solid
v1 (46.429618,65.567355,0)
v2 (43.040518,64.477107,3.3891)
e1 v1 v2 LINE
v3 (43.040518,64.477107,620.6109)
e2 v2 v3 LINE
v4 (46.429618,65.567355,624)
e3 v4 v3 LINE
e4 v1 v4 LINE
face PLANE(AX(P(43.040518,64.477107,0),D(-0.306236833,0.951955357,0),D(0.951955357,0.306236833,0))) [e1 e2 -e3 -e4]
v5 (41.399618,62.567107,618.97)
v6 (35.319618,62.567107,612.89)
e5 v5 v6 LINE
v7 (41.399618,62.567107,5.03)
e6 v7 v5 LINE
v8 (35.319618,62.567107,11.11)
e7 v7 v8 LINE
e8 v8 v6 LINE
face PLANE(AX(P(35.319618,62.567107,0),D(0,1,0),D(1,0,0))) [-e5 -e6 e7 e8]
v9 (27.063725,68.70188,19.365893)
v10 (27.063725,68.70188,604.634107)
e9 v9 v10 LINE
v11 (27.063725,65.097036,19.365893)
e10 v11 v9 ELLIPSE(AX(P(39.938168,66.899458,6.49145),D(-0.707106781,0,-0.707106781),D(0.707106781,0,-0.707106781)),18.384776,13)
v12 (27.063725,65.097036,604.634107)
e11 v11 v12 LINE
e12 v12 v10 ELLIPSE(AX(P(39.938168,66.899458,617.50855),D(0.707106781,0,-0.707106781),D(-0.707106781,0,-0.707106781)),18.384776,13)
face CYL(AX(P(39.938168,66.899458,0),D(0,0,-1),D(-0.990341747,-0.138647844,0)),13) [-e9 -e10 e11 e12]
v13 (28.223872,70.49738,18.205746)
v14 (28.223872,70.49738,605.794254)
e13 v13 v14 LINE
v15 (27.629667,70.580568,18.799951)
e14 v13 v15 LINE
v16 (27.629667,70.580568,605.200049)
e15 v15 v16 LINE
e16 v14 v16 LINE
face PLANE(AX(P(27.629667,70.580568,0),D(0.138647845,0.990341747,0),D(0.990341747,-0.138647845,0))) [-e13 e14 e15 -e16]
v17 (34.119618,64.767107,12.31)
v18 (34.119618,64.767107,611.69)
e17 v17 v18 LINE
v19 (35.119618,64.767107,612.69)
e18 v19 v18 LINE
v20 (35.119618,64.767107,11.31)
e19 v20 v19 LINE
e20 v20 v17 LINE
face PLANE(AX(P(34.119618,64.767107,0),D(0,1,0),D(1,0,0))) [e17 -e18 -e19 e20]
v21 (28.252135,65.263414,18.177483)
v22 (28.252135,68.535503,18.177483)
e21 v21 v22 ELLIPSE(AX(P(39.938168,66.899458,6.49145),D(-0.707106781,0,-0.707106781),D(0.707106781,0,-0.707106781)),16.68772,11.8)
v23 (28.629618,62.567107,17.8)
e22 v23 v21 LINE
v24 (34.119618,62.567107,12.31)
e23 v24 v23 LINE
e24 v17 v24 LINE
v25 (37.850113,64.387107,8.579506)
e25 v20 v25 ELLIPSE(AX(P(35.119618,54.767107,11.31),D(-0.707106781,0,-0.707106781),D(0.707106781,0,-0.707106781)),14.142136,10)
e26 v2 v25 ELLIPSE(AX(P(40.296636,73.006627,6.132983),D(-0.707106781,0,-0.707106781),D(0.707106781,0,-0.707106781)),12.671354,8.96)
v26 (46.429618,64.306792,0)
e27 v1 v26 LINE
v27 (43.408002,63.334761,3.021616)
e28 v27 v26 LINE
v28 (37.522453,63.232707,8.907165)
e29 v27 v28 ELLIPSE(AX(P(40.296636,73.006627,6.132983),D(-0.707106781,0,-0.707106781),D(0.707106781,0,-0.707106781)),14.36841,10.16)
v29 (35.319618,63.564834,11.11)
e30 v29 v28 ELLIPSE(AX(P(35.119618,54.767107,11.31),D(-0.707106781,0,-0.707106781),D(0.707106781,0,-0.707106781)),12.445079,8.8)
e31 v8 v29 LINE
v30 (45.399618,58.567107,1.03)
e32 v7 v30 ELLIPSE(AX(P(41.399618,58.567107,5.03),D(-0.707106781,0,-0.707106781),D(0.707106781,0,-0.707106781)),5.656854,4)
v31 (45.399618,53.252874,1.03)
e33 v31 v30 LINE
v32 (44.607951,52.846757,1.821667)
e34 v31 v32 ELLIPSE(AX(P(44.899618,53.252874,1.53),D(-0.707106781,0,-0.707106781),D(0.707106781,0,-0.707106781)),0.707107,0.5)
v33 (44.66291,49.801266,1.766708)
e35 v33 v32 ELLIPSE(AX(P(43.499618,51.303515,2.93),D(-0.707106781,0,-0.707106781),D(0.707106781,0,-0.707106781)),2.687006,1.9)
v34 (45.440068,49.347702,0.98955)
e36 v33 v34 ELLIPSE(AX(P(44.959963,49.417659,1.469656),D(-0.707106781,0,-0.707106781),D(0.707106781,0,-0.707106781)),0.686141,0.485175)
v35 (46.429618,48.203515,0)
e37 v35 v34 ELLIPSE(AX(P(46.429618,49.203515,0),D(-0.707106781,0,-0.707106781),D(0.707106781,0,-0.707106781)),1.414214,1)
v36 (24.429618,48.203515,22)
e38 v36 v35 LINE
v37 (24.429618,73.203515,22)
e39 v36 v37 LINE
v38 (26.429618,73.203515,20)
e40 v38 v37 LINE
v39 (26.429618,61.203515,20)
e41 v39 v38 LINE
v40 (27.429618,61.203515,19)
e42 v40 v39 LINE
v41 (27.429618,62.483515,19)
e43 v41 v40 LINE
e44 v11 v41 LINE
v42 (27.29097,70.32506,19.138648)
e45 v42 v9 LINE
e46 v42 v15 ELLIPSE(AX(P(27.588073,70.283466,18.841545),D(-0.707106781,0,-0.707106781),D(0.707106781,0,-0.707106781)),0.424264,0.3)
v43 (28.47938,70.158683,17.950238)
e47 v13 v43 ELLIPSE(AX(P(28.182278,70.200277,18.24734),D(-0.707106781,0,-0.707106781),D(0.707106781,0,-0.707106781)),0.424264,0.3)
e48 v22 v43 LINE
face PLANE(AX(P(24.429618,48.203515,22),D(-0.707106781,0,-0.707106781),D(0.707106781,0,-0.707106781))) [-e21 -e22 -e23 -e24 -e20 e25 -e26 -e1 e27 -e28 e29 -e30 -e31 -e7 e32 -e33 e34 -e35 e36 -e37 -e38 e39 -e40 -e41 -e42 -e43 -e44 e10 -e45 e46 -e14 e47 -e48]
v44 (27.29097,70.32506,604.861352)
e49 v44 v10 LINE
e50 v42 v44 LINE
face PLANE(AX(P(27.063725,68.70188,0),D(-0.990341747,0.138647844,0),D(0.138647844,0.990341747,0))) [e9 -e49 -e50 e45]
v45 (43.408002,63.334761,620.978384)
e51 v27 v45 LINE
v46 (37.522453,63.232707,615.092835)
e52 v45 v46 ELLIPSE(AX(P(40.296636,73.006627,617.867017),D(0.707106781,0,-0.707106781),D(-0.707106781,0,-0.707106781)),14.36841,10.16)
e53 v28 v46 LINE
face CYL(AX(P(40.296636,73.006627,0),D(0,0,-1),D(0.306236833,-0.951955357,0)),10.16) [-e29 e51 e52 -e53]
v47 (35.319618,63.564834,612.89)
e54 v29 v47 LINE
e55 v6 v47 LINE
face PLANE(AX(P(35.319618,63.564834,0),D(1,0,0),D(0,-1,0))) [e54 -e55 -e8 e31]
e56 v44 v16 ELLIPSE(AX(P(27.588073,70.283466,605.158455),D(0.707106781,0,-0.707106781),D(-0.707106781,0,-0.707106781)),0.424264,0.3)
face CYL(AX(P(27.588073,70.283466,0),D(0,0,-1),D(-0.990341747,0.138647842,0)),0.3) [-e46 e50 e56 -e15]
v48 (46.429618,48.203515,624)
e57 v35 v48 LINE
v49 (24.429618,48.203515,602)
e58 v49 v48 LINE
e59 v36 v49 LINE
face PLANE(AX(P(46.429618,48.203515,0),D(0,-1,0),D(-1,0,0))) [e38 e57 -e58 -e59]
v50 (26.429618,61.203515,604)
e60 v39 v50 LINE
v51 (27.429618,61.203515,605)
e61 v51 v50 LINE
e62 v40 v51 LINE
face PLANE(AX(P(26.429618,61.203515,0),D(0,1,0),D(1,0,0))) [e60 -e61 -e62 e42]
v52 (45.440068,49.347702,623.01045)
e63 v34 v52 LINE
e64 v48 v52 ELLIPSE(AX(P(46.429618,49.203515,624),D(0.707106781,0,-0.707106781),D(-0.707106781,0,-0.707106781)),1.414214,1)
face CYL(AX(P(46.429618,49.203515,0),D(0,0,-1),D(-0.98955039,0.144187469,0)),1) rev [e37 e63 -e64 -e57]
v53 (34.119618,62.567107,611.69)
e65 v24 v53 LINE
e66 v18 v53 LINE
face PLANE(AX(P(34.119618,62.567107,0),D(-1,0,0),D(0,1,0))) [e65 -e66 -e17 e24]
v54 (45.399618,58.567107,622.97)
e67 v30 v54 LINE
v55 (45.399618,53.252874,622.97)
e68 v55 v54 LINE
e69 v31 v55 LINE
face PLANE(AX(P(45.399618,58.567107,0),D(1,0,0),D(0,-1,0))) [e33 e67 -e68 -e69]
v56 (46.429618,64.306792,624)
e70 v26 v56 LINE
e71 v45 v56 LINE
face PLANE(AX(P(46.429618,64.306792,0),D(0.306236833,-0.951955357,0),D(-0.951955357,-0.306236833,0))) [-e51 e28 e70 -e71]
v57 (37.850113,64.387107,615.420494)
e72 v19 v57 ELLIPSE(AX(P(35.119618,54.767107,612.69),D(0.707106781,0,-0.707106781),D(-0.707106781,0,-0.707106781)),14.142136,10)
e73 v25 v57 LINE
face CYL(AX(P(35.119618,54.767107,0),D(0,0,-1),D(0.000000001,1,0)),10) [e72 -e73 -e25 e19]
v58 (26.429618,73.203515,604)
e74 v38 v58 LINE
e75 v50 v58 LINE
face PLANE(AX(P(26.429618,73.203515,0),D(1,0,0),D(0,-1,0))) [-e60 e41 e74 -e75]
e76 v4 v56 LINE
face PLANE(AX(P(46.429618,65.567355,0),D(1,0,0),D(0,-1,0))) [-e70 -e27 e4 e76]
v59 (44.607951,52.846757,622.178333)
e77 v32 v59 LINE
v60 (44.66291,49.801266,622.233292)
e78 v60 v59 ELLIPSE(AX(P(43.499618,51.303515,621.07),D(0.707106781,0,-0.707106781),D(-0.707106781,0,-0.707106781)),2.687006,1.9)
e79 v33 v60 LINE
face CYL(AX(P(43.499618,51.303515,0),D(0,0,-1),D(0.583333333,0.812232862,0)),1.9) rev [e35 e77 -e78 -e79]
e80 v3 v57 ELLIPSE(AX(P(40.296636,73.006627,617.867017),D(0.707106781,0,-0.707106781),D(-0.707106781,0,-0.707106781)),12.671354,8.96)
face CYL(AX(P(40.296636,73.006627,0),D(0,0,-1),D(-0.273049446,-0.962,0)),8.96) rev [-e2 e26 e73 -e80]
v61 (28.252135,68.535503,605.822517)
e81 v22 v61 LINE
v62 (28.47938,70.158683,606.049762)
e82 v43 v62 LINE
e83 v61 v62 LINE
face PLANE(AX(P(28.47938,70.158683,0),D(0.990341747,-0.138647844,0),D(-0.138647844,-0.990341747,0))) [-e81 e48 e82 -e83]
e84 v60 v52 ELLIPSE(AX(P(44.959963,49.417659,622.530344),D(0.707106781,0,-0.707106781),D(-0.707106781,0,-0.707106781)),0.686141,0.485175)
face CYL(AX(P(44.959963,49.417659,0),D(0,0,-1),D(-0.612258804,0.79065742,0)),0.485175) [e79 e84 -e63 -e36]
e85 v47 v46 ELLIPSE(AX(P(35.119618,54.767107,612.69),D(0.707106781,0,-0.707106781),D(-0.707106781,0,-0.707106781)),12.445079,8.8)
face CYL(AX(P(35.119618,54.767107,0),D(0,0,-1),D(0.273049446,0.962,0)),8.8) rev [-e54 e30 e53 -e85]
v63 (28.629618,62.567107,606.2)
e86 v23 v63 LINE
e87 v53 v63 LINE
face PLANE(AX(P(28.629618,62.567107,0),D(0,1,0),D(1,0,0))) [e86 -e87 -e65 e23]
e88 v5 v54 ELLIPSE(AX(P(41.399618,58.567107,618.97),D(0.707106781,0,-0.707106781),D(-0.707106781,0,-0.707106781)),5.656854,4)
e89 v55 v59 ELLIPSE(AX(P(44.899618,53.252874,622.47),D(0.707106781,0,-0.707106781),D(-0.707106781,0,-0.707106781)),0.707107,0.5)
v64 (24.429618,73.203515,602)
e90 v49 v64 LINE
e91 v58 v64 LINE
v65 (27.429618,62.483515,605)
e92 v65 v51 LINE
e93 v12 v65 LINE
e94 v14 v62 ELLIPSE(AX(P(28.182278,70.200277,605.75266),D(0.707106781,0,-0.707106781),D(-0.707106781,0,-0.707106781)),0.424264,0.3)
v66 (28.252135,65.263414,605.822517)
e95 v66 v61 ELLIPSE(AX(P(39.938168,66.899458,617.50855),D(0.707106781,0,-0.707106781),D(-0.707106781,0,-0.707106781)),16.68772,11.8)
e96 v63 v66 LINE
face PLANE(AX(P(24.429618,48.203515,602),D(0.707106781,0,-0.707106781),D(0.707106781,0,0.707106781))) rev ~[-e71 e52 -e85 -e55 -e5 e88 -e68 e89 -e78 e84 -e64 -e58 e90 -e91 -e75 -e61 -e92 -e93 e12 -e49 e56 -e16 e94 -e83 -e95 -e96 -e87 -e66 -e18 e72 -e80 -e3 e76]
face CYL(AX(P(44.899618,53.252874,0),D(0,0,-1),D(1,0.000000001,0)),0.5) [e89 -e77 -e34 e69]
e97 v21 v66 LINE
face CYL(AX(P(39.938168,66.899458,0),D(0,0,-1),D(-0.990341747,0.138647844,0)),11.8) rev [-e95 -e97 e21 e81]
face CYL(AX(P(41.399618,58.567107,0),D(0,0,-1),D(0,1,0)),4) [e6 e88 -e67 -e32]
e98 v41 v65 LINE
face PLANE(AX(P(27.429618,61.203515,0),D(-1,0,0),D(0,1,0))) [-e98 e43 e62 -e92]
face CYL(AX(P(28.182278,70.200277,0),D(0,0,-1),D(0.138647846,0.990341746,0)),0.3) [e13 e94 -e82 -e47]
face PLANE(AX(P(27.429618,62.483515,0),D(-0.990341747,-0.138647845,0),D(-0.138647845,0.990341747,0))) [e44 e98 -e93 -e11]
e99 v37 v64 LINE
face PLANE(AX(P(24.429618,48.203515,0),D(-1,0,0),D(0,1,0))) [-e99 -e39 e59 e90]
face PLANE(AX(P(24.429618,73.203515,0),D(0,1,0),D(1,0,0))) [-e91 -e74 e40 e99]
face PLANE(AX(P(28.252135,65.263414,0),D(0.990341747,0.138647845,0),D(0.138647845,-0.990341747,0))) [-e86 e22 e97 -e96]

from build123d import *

# Parameters (mm, degrees)
EXTRUDE1_DEPTH = 624
EXTRUDE2_DEPTH = 30


with BuildPart() as part:
    # Sketch2 → Extrude1 (new body)
    with BuildSketch(Plane.XY):
        with BuildLine():
            Line((27.429618111, 61.203514875), (27.429618111, 62.483514875))
            Line((27.429618111, 62.483514875), (27.063725093, 65.097036429))
            ThreePointArc((27.063725093, 65.097036429), (26.9381678, 66.899458408), (27.063725093, 68.701880387))
            Line((27.063725093, 68.701880387), (27.290970266, 70.325060195))
            ThreePointArc((27.290970266, 70.325060195), (27.40740123, 70.522960701), (27.629667144, 70.580568366))
            Line((27.629667144, 70.580568366), (28.223872192, 70.497379659))
            ThreePointArc((28.223872192, 70.497379659), (28.421772697, 70.380948695), (28.479380362, 70.158682782))
            Line((28.479380362, 70.158682782), (28.252135189, 68.535502974))
            ThreePointArc((28.252135189, 68.535502974), (28.1381678, 66.899458408), (28.252135189, 65.263413843))
            Line((28.252135189, 65.263413843), (28.629618111, 62.56710726))
            Line((28.629618111, 62.56710726), (34.119618111, 62.56710726))
            Line((34.119618111, 62.56710726), (34.119618111, 64.76710726))
            Line((34.119618111, 64.76710726), (35.119618111, 64.76710726))
            ThreePointArc((35.119618111, 64.76710726), (36.498022986, 64.671651671), (37.850112572, 64.38710726))
            ThreePointArc((37.850112572, 64.38710726), (40.451975855, 64.047973934), (43.040517634, 64.47710726))
            Line((43.040517634, 64.47710726), (46.429618111, 65.567355231))
            Line((46.429618111, 65.567355231), (46.429618111, 64.306791917))
            Line((46.429618111, 64.306791917), (43.408001834, 63.334760831))
            ThreePointArc((43.408001834, 63.334760831), (40.472780352, 62.848154292), (37.522453236, 63.23270726))
            ThreePointArc((37.522453236, 63.23270726), (36.431587911, 63.468758554), (35.319618111, 63.564834239))
            Line((35.319618111, 63.564834239), (35.319618111, 62.56710726))
            Line((35.319618111, 62.56710726), (41.399618111, 62.56710726))
            ThreePointArc((41.399618111, 62.56710726), (44.228045236, 61.395534384), (45.399618111, 58.56710726))
            Line((45.399618111, 58.56710726), (45.399618111, 53.252873744))
            ThreePointArc((45.399618111, 53.252873744), (45.127835843, 52.807995483), (44.607951444, 52.846757313))
            ThreePointArc((44.607951444, 52.846757313), (41.599927405, 51.269233396), (44.662909839, 49.801265776))
            ThreePointArc((44.662909839, 49.801265776), (45.204517239, 49.836690545), (45.440067721, 49.347702344))
            ThreePointArc((45.440067721, 49.347702344), (45.673249329, 48.549369428), (46.429618111, 48.203514875))
            Line((46.429618111, 48.203514875), (24.429618111, 48.203514875))
            Line((24.429618111, 48.203514875), (24.429618111, 73.203514875))
            Line((24.429618111, 73.203514875), (26.429618111, 73.203514875))
            Line((26.429618111, 73.203514875), (26.429618111, 61.203514875))
            Line((26.429618111, 61.203514875), (27.429618111, 61.203514875))
        make_face()
    extrude(amount=EXTRUDE1_DEPTH)

    # Sketch3 → Extrude2 (cut)
    with BuildSketch(Plane.XZ.offset(-48.203514875)):
        Polygon((46.429618111, 624), (24.429618111, 624), (24.429618111, 602), align=None)
        Polygon((46.429618111, 0), (24.429618111, 0), (24.429618111, 22), align=None)
    extrude(amount=-EXTRUDE2_DEPTH, mode=Mode.SUBTRACT)


solid = part.part
